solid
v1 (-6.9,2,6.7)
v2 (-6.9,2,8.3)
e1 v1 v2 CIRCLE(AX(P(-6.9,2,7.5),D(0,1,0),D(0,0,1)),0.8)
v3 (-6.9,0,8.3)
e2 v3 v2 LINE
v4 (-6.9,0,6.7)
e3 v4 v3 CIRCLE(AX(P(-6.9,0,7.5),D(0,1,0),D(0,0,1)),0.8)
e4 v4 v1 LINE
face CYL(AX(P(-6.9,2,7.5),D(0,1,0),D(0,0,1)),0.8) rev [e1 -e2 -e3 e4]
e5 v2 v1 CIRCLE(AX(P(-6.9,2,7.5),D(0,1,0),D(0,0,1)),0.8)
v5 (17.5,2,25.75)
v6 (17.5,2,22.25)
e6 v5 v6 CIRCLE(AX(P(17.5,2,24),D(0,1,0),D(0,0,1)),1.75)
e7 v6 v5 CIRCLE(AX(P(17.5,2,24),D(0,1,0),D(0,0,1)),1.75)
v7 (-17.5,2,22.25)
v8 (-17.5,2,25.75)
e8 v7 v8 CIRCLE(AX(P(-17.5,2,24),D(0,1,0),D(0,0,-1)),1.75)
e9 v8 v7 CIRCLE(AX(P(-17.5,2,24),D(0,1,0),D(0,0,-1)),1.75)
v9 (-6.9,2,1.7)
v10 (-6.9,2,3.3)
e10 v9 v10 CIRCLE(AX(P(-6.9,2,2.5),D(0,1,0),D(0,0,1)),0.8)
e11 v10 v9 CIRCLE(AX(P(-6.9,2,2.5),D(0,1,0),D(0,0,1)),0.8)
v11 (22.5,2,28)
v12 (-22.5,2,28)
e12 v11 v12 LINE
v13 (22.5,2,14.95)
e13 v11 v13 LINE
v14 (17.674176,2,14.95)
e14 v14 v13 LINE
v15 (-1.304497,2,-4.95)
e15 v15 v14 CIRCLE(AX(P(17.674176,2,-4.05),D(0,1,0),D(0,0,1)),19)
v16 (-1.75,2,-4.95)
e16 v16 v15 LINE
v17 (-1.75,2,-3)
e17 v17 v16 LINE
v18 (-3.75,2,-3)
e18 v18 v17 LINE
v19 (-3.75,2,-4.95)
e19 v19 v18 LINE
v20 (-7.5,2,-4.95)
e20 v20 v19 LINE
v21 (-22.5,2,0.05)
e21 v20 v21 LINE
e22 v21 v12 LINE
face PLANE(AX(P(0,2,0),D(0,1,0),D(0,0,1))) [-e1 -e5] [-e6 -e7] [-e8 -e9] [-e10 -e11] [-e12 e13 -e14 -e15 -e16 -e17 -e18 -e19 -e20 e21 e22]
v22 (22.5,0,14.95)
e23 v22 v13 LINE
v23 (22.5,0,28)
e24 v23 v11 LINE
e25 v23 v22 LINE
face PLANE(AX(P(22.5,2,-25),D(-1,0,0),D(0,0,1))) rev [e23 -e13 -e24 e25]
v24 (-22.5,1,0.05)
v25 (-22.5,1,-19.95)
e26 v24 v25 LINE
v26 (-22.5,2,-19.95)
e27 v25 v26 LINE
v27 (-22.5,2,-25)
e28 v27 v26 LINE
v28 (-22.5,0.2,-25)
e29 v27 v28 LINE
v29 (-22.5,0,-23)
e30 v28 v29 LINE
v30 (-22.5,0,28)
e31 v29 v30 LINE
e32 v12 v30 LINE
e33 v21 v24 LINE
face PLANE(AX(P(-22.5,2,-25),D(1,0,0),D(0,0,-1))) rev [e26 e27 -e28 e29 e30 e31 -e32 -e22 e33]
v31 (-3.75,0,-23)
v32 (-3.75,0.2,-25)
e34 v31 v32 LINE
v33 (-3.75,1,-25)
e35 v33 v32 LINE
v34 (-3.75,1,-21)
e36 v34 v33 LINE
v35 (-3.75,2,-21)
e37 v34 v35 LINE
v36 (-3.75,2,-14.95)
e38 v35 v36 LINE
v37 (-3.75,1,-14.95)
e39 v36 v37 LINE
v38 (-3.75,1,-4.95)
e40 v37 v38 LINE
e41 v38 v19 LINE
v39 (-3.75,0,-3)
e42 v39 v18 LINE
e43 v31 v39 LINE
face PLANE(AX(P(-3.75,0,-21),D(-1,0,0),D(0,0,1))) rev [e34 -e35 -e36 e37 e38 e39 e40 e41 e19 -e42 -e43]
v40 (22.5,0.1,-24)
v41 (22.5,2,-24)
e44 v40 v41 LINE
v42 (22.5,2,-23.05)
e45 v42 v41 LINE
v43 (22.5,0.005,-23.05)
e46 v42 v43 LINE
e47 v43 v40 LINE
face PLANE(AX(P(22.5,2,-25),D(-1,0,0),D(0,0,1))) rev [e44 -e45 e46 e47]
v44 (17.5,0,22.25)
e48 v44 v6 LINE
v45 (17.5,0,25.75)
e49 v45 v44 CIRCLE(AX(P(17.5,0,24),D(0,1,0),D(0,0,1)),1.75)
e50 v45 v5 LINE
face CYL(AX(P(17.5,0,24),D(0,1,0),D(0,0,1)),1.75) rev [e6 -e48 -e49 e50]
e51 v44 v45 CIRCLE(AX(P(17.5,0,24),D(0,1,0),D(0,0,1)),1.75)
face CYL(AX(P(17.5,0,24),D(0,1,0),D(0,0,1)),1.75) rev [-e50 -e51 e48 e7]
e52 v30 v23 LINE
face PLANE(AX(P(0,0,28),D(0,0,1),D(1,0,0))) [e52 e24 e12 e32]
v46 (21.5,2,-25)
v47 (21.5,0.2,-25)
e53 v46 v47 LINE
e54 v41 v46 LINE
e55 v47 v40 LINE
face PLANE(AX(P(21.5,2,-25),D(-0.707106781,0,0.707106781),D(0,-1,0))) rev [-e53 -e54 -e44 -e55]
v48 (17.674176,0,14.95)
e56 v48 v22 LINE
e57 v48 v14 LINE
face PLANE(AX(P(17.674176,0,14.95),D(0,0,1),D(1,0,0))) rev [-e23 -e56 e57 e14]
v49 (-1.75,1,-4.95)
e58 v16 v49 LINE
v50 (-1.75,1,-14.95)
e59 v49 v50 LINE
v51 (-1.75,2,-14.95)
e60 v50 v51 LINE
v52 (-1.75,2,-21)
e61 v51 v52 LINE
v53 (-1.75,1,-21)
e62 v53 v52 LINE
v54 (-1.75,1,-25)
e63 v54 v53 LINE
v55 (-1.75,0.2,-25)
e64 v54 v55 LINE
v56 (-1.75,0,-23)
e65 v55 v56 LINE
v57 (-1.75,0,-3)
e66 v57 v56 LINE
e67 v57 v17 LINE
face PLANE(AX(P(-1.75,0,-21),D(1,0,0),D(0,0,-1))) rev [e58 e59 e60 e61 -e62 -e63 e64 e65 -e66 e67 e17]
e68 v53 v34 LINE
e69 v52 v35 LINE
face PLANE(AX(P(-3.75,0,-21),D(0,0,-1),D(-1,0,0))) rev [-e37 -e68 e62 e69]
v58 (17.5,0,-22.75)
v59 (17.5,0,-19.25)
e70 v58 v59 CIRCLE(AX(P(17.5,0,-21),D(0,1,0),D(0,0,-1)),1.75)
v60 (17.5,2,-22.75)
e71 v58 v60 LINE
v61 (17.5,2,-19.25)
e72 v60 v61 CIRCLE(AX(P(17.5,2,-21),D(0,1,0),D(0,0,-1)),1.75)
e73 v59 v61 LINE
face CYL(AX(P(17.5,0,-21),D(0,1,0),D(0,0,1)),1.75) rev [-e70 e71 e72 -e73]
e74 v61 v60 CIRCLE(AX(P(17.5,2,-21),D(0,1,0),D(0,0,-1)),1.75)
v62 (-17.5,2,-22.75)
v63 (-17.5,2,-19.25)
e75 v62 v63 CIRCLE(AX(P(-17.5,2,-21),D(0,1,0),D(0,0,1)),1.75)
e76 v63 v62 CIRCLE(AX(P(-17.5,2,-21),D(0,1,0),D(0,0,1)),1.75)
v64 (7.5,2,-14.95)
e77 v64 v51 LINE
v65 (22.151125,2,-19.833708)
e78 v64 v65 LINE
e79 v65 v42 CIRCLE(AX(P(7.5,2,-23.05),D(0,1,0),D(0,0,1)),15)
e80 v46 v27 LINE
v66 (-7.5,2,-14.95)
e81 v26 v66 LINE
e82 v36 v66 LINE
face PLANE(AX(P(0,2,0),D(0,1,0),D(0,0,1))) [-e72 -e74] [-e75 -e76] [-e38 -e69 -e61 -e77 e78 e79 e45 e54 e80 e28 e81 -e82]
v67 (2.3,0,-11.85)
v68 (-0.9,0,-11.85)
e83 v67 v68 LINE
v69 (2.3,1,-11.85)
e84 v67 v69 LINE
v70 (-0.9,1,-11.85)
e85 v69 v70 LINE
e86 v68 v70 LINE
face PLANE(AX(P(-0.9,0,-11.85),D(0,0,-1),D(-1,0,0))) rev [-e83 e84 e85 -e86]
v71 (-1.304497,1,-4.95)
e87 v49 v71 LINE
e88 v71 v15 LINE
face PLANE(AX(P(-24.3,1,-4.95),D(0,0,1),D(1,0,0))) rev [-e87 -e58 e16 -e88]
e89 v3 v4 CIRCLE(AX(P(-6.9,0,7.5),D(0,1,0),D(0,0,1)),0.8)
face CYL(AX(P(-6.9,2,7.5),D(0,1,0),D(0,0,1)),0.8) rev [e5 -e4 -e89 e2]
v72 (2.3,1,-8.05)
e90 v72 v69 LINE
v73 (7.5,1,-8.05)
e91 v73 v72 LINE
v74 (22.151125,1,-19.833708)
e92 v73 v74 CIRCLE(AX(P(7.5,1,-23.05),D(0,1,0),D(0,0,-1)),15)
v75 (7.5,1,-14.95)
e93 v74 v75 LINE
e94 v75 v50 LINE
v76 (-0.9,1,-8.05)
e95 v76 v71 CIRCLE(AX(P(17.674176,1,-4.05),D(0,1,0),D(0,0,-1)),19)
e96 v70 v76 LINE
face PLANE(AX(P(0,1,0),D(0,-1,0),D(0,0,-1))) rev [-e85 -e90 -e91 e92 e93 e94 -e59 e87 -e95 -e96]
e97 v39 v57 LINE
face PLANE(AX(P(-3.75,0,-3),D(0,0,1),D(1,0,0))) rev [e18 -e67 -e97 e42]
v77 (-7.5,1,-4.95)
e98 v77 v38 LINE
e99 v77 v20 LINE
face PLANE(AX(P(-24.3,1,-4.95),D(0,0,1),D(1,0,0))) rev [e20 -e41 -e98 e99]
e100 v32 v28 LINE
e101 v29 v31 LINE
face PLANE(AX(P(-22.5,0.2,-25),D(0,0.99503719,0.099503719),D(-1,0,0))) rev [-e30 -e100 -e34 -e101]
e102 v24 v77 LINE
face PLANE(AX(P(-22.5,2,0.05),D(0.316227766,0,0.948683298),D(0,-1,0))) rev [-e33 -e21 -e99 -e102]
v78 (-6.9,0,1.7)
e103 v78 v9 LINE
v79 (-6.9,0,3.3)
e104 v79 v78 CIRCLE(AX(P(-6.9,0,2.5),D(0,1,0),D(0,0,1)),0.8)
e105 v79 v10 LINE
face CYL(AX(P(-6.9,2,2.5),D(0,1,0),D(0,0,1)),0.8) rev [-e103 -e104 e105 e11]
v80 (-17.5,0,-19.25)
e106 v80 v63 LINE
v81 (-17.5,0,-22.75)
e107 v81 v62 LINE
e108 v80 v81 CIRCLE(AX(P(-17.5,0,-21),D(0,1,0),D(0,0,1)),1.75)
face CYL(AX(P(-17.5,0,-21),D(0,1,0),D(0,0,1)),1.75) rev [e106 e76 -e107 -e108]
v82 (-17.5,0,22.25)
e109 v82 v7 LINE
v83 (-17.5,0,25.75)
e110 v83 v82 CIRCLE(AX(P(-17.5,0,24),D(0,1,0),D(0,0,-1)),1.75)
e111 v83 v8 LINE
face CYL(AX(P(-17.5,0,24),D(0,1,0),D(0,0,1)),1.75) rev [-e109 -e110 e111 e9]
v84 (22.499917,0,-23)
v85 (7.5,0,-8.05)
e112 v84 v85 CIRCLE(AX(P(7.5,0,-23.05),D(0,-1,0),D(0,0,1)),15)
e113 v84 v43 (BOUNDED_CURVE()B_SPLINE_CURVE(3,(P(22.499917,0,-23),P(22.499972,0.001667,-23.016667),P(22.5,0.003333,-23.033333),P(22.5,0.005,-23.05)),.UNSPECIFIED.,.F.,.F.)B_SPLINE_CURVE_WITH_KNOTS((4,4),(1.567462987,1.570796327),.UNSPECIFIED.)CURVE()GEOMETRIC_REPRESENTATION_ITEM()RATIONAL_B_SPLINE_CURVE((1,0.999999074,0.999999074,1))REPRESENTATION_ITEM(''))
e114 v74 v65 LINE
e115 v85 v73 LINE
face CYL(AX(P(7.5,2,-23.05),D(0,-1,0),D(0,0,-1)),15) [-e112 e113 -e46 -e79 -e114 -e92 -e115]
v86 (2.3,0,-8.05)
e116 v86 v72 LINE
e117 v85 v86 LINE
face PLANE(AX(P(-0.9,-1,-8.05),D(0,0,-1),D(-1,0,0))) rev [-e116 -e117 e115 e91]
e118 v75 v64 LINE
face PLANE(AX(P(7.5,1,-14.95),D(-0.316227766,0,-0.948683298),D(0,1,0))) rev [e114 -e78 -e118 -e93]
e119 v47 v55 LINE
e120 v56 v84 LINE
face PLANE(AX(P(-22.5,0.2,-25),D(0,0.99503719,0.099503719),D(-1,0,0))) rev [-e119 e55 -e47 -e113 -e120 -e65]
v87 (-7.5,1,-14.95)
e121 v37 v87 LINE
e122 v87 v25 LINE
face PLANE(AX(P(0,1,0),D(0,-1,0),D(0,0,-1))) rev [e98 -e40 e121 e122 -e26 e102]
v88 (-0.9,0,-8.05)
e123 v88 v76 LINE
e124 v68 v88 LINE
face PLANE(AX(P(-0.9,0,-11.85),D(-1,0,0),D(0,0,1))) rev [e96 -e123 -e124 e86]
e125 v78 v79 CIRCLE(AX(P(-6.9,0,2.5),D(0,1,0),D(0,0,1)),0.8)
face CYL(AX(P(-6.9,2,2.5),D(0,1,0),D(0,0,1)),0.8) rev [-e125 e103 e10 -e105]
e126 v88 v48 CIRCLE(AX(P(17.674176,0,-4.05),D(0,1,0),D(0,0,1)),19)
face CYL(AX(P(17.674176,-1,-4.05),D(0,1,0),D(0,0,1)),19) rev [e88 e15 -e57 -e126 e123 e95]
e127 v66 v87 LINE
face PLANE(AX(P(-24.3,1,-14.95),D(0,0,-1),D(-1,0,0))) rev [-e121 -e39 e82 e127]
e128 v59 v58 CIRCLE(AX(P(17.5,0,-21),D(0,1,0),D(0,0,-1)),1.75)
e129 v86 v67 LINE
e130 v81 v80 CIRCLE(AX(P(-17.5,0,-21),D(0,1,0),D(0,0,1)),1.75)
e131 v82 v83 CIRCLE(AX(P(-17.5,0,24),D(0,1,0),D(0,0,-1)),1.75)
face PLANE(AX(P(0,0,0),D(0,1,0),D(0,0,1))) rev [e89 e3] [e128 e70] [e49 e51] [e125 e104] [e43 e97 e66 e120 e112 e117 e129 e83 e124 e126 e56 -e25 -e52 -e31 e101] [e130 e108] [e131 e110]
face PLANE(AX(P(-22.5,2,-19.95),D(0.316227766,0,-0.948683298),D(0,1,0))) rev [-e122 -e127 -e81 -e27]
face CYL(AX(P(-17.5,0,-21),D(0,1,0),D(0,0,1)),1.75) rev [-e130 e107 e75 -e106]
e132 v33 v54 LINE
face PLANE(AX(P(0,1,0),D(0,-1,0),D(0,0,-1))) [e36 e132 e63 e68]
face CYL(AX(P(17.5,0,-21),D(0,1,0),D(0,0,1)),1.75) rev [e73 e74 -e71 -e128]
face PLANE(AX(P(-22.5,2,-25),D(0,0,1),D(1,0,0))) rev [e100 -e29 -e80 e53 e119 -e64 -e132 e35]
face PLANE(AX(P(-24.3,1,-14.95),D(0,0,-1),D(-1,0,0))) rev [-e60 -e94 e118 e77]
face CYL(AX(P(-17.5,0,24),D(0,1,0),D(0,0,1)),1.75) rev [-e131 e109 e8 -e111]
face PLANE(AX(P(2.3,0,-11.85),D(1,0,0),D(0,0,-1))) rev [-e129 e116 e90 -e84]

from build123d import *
from OCP.BRepFilletAPI import BRepFilletAPI_MakeChamfer

# Parameters (mm, degrees)
SKETCH1_W             = 45
SKETCH1_H             = 50
BOSS_EXTRUDE1_DEPTH   = 2
SKETCH2_W             = 3.2
SKETCH2_H             = 3.8
CUT_EXTRUDE1_DEPTH    = 34.693471178
SKETCH3_W             = 2
SKETCH3_H             = 18
CUT_EXTRUDE2_DEPTH    = 34.693471178
SKETCH4_W             = 2
SKETCH4_H             = 4
CUT_EXTRUDE3_DEPTH    = 1
CUT_EXTRUDE4_DEPTH    = 3
SKETCH6_W             = 46.8
SKETCH6_H             = 10
CUT_EXTRUDE5_DEPTH    = 1
CHAMFER1_SIZE         = 15
CHAMFER1_SIZE2        = 5
CHAMFER2_SIZE         = 5
CHAMFER2_SIZE2        = 15
SKETCH8_W             = 45
SKETCH8_H             = 2
BOSS_EXTRUDE2_DEPTH   = 3
SKETCH7_R             = 1.75
CUT_EXTRUDE6_DEPTH    = 36.975686234
FILLET2_R             = 15
CHAMFER4_SIZE         = 2
CHAMFER4_SIZE2        = 0.2
SKETCH10_W            = 4.825824379
SKETCH10_H            = 2.951447422
CUT_EXTRUDE7_DEPTH    = 36.975686234
CHAMFER5_SIZE         = 1
M2_TAPPED_HOLE1_D     = 1.6
M2_TAPPED_HOLE1_DEPTH = 5.2
M2_TAPPED_HOLE1_TIP   = 0.480688495


with BuildPart() as part:
    # Sketch1 → Boss-Extrude1 (new body)
    with BuildSketch(Plane(origin=(0, 0, 0), x_dir=(1, 0, 0), z_dir=(0, 1, 0))):
        Rectangle(SKETCH1_W, SKETCH1_H)
    extrude(amount=BOSS_EXTRUDE1_DEPTH)

    # Sketch2 → Cut-Extrude1 (cut, through all)
    with BuildSketch(Plane(origin=(0, 2, 0), x_dir=(1, 0, 0), z_dir=(0, 1, 0))):
        with Locations((0.7, 9.95)):
            Rectangle(SKETCH2_W, SKETCH2_H)
    extrude(amount=-CUT_EXTRUDE1_DEPTH, mode=Mode.SUBTRACT)

    # Sketch3 → Cut-Extrude2 (cut, through all)
    with BuildSketch(Plane(origin=(0, 2, 0), x_dir=(1, 0, 0), z_dir=(0, 1, 0))):
        with Locations((-2.75, 12)):
            Rectangle(SKETCH3_W, SKETCH3_H)
    extrude(amount=-CUT_EXTRUDE2_DEPTH, mode=Mode.SUBTRACT)

    # Sketch4 → Cut-Extrude3 (cut)
    with BuildSketch(Plane.XZ):
        with Locations((-2.75, -23)):
            Rectangle(SKETCH4_W, SKETCH4_H)
    extrude(amount=-CUT_EXTRUDE3_DEPTH, mode=Mode.SUBTRACT)

    # Sketch5 → Cut-Extrude4 (cut)
    with BuildSketch(Plane(origin=(0, 2, 0), x_dir=(1, 0, 0), z_dir=(0, 1, 0))):
        with BuildLine():
            Line((-0.9, 8.05), (26.461433113, 8.05))
            Line((26.461433113, 8.05), (36.248351242, 8.05))
            ThreePointArc((36.248351242, 8.05), (17.674175621, -14.95), (-0.9, 8.05))
        make_face()
    extrude(amount=-CUT_EXTRUDE4_DEPTH, mode=Mode.SUBTRACT)

    # Sketch6 → Cut-Extrude5 (cut)
    with BuildSketch(Plane(origin=(0, 2, 0), x_dir=(1, 0, 0), z_dir=(0, 1, 0))):
        with Locations((-0.9, 9.95)):
            Rectangle(SKETCH6_W, SKETCH6_H)
    extrude(amount=-CUT_EXTRUDE5_DEPTH, mode=Mode.SUBTRACT)

    # Chamfer1: one chamfer whose edges measure the first distance from different faces: ONE call of the kernel's chamfer builder (chamfer() names one face for all edges)
    chamfer1_edges_1 = [part.edges().sort_by_distance(p)[0] for p in [
        (-22.5, 1.5, -14.95),
    ]]
    chamfer1_side_1 = [part.faces().sort_by_distance(p)[0] for p in [
        (-13.125, 1.5, -14.95),
    ]]
    chamfer1_edges_2 = [part.edges().sort_by_distance(p)[0] for p in [
        (-22.5, 1.5, -4.95),
    ]]
    chamfer1_side_2 = [part.faces().sort_by_distance(p)[0] for p in [
        (-13.125, 1.5, -4.95),
    ]]
    chamfer1 = BRepFilletAPI_MakeChamfer(part.part.solid().wrapped)
    for e in chamfer1_edges_1:
        chamfer1.Add(CHAMFER1_SIZE, CHAMFER1_SIZE2, e.wrapped, chamfer1_side_1[0].wrapped)  # the first distance lies on this face
    for e in chamfer1_edges_2:
        chamfer1.Add(CHAMFER1_SIZE, CHAMFER1_SIZE2, e.wrapped, chamfer1_side_2[0].wrapped)  # the first distance lies on this face
    add(Compound.cast(chamfer1.Shape()), mode=Mode.REPLACE)

    # Chamfer2
    chamfer2_edges = [part.edges().sort_by_distance(p)[0] for p in [
        (22.5, 1.5, -14.95),
    ]]
    chamfer2_side = [part.faces().sort_by_distance(p)[0] for p in [
        (22.5, 0.872222222, -17.809166667),
    ]]
    chamfer(chamfer2_edges, length=CHAMFER2_SIZE, length2=CHAMFER2_SIZE2, reference=chamfer2_side[0])

    # Sketch8 → Boss-Extrude2 (add)
    with BuildSketch(Plane.XY.offset(25)):
        with Locations((0, 1)):
            Rectangle(SKETCH8_W, SKETCH8_H)
    extrude(amount=BOSS_EXTRUDE2_DEPTH)

    # Sketch7 → Cut-Extrude6 (cut, through all)
    with BuildSketch(Plane(origin=(0, 2, 0), x_dir=(1, 0, 0), z_dir=(0, 1, 0))):
        with Locations(Location((-17.5, 21, 0), (0, 0, 270))):
            Circle(SKETCH7_R)
        with Locations(Location((17.5, 21, 0), (0, 0, 90))):
            Circle(SKETCH7_R)
        with Locations(Location((17.5, -24, 0), (0, 0, 270))):
            Circle(SKETCH7_R)
        with Locations(Location((-17.5, -24, 0), (0, 0, 90))):
            Circle(SKETCH7_R)
    extrude(amount=-CUT_EXTRUDE6_DEPTH, mode=Mode.SUBTRACT)

    # Fillet2
    fillet2_edges = [part.edges().sort_by_distance(p)[0] for p in [
        (22.5, 0.5, -8.05),
    ]]
    fillet(fillet2_edges, radius=FILLET2_R)

    # Chamfer4
    chamfer4_edges = [part.edges().sort_by_distance(p)[0] for p in [
        (10.375, 0, -25),
        (-13.125, 0, -25),
    ]]
    chamfer4_side = [part.faces().sort_by_distance(p)[0] for p in [
        (-3.590988943, 0, 2.118757262),
    ]]
    chamfer(chamfer4_edges, length=CHAMFER4_SIZE, length2=CHAMFER4_SIZE2, reference=chamfer4_side[0])

    # Sketch10 → Cut-Extrude7 (cut, through all)
    with BuildSketch(Plane(origin=(0, 2, 0), x_dir=(1, 0, 0), z_dir=(0, 1, 0))):
        with Locations((20.087087811, -13.474276289)):
            Rectangle(SKETCH10_W, SKETCH10_H)
    extrude(amount=-CUT_EXTRUDE7_DEPTH, mode=Mode.SUBTRACT)

    # Chamfer5
    chamfer5_edges = [part.edges().sort_by_distance(p)[0] for p in [
        (22.5, 1.1, -25),
    ]]
    chamfer(chamfer5_edges, length=CHAMFER5_SIZE)

    # M2 Tapped Hole1
    with Locations(Plane(origin=(0, 2, 0), x_dir=(1, 0, 0), z_dir=(0, 1, 0))):
        with Locations((-6.9, -7.5), (-6.9, -2.5)):
            Hole(M2_TAPPED_HOLE1_D / 2, depth=M2_TAPPED_HOLE1_DEPTH)
            with Locations((0, 0, -(M2_TAPPED_HOLE1_DEPTH + M2_TAPPED_HOLE1_TIP / 2))):  # 118° drill point
                Cone(0, M2_TAPPED_HOLE1_D / 2, M2_TAPPED_HOLE1_TIP, mode=Mode.SUBTRACT)


solid = part.part
